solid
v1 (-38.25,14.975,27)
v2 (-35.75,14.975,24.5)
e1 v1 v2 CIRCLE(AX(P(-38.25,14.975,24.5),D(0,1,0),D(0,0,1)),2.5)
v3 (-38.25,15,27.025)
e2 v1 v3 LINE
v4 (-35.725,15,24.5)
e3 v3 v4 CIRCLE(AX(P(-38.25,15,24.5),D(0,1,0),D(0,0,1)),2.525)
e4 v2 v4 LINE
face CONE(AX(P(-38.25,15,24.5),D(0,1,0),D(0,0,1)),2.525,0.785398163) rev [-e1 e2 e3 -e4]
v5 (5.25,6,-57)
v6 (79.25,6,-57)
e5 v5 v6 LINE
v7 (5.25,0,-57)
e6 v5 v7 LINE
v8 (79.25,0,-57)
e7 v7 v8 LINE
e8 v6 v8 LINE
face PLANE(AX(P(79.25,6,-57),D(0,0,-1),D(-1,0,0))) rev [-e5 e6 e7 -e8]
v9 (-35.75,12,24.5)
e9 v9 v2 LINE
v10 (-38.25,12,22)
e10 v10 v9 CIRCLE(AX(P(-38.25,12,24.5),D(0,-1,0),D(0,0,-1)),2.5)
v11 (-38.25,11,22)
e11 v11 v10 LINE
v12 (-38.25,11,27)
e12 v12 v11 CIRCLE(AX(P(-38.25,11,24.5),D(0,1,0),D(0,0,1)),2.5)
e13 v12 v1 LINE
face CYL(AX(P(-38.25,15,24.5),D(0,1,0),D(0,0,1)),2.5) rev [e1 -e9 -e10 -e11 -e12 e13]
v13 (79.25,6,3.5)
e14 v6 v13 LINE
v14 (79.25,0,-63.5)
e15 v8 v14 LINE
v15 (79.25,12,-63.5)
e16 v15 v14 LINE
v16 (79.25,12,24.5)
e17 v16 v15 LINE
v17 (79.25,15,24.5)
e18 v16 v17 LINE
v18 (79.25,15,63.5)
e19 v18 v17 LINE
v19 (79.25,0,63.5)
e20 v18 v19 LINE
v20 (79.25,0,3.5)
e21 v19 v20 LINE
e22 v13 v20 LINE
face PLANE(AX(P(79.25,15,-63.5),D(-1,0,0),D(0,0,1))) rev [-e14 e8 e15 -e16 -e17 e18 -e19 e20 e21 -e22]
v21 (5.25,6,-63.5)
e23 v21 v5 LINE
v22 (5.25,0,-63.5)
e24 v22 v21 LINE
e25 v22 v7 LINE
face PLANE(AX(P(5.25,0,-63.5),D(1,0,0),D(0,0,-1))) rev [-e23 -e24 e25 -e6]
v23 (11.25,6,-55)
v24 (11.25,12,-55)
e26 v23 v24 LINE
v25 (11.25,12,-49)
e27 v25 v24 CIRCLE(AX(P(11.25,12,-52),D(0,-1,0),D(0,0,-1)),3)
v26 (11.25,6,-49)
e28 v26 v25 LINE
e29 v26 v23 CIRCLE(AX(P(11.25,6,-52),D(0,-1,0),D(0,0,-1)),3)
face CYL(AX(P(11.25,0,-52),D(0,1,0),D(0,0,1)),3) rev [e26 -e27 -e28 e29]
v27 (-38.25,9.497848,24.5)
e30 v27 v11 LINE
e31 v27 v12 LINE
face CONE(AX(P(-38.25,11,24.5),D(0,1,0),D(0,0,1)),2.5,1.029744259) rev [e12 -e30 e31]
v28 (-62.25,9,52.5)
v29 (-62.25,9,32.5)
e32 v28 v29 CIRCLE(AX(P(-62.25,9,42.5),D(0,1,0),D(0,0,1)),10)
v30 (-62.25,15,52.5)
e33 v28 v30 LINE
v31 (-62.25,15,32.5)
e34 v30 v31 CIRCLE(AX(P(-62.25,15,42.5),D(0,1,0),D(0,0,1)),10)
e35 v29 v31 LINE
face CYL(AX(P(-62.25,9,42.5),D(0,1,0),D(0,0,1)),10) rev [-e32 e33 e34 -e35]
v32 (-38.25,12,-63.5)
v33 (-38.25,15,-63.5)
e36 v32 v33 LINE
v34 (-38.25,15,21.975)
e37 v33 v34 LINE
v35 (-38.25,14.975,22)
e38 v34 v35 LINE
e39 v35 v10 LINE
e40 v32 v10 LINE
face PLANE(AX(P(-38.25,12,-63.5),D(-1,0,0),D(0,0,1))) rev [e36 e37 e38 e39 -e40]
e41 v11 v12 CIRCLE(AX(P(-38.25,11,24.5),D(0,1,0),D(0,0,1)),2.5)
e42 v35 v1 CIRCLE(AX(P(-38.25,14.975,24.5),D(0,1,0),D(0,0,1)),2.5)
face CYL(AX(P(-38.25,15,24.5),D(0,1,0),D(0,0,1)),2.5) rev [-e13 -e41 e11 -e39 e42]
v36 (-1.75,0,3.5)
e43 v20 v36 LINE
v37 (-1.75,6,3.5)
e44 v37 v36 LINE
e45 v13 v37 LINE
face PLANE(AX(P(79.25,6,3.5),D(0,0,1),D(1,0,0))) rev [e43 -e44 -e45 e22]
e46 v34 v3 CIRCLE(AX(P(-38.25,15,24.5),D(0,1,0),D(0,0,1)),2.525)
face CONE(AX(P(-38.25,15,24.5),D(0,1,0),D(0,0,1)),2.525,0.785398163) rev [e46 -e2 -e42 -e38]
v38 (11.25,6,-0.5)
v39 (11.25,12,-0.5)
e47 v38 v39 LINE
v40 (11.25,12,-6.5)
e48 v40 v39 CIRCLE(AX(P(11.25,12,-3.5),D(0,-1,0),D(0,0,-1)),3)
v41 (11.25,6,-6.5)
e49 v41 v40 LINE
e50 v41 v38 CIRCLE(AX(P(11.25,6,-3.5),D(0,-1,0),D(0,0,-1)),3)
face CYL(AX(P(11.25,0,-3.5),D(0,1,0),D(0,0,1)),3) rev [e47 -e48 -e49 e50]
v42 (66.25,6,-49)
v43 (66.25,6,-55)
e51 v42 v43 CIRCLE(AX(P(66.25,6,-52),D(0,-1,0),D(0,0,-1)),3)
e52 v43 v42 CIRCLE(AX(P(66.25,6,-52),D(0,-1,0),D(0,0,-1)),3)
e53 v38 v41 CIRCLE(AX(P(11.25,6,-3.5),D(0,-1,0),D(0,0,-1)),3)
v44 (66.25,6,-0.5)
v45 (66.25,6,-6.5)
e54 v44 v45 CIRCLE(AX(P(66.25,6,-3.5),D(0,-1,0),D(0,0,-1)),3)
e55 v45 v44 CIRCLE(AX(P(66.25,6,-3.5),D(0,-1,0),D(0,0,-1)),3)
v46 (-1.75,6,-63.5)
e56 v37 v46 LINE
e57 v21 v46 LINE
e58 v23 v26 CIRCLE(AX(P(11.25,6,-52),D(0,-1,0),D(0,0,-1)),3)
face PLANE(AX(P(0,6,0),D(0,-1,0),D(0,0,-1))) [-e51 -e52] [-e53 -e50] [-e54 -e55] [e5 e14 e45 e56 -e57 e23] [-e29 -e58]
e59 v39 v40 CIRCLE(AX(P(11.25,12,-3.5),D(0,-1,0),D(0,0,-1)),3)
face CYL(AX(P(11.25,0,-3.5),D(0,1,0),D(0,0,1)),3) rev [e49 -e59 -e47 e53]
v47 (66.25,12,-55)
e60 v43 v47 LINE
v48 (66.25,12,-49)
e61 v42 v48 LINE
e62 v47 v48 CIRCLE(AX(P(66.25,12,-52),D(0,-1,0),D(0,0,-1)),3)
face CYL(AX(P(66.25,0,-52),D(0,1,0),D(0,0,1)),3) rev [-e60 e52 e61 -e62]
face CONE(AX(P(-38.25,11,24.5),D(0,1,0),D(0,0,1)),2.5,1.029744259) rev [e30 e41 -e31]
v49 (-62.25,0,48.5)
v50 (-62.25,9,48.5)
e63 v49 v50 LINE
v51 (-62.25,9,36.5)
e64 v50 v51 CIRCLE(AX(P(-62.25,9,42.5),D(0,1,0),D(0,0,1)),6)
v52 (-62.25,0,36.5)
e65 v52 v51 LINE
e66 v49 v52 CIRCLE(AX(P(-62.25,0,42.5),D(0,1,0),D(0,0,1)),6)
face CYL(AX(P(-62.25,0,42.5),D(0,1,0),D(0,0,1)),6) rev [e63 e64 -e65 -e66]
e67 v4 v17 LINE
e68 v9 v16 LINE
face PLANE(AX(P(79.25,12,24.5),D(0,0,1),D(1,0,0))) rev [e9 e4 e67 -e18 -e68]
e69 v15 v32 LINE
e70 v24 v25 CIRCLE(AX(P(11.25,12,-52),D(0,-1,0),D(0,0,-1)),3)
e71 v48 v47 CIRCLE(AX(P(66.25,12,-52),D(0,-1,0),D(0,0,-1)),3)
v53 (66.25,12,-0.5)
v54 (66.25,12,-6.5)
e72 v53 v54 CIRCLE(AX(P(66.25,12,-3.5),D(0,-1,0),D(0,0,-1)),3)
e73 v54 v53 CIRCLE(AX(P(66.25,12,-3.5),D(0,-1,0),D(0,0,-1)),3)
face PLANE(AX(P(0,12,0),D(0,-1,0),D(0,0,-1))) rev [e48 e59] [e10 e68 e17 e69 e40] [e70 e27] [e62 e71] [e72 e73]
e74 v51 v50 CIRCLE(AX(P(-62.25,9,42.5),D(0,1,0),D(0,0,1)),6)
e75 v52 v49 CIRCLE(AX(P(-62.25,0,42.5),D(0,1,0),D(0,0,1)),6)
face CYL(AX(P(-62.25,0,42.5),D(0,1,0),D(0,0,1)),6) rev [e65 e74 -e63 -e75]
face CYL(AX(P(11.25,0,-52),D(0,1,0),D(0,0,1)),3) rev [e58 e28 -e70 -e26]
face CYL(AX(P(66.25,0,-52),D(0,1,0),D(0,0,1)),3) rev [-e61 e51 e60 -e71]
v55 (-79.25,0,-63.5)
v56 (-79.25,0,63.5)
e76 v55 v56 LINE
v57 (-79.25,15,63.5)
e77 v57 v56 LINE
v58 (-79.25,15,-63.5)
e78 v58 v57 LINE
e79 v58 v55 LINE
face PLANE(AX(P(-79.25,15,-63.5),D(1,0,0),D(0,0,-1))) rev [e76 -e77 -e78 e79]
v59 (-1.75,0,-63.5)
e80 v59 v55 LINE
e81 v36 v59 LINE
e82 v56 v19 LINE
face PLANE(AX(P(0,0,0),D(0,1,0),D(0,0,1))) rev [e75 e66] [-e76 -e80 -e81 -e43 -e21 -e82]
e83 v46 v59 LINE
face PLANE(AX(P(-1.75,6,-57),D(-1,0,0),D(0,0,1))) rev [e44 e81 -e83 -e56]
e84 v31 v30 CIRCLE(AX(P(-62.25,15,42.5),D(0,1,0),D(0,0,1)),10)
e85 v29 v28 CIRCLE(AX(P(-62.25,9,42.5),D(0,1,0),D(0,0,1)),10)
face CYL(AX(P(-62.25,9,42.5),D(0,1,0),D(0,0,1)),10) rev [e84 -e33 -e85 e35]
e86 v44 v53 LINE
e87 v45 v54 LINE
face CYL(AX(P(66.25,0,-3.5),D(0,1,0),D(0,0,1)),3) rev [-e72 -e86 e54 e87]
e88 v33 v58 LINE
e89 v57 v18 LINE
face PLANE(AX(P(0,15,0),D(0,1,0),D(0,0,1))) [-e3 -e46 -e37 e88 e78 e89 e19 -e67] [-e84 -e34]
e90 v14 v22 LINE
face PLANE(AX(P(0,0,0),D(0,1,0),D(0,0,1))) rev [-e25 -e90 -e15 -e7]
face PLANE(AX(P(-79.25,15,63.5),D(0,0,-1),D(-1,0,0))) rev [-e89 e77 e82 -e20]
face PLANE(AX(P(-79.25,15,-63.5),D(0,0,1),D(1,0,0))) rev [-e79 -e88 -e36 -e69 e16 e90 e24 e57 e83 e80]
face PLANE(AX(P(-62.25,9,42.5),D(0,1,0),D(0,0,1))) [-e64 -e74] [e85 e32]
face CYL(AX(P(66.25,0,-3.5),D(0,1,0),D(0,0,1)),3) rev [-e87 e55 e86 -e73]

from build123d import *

# Parameters (mm, degrees)
SKETCH1_W                              = 158.5
SKETCH1_H                              = 127
BOSS_EXTRUDE1_DEPTH                    = 15
SKETCH2_W                              = 117.5
SKETCH2_H                              = 88
CUT_EXTRUDE1_DEPTH                     = 3
SKETCH3_W                              = 81
SKETCH3_H                              = 60.5
CUT_EXTRUDE2_DEPTH                     = 6
SKETCH4_W                              = 7
SKETCH4_H                              = 6
CUT_EXTRUDE3_DEPTH                     = 103.653847955
SKETCH5_R                              = 3
CUT_EXTRUDE4_DEPTH                     = 103.653847955
SKETCH6_R                              = 10
CUT_EXTRUDE5_DEPTH                     = 6
SKETCH7_R                              = 6
CUT_EXTRUDE6_DEPTH                     = 102.950049044
F_5_0MM_BLIND_DOWEL_HOLE_1_D           = 5
F_5_0MM_BLIND_DOWEL_HOLE_1_DEPTH       = 4
F_5_0MM_BLIND_DOWEL_HOLE_1_CSINK_D     = 5.05
F_5_0MM_BLIND_DOWEL_HOLE_1_CSINK_ANGLE = 90
F_5_0MM_BLIND_DOWEL_HOLE_1_TIP         = 1.502151548


with BuildPart() as part:
    # Sketch1 → Boss-Extrude1 (new body)
    with BuildSketch(Plane(origin=(0, 0, 0), x_dir=(1, 0, 0), z_dir=(0, 1, 0))):
        Rectangle(SKETCH1_W, SKETCH1_H)
    extrude(amount=BOSS_EXTRUDE1_DEPTH)

    # Sketch2 → Cut-Extrude1 (cut)
    with BuildSketch(Plane(origin=(0, 15, 0), x_dir=(1, 0, 0), z_dir=(0, 1, 0))):
        with Locations((20.5, 19.5)):
            Rectangle(SKETCH2_W, SKETCH2_H)
    extrude(amount=-CUT_EXTRUDE1_DEPTH, mode=Mode.SUBTRACT)

    # Sketch3 → Cut-Extrude2 (cut)
    with BuildSketch(Plane.XZ):
        with Locations((38.75, -26.75)):
            Rectangle(SKETCH3_W, SKETCH3_H)
    extrude(amount=-CUT_EXTRUDE2_DEPTH, mode=Mode.SUBTRACT)

    # Sketch4 → Cut-Extrude3 (cut, through all)
    with BuildSketch(Plane.XY):
        with Locations((1.75, 3)):
            Rectangle(SKETCH4_W, SKETCH4_H)
    extrude(amount=-CUT_EXTRUDE3_DEPTH, mode=Mode.SUBTRACT)

    # Sketch5 → Cut-Extrude4 (cut, through all)
    with BuildSketch(Plane(origin=(0, 15, 0), x_dir=(1, 0, 0), z_dir=(0, 1, 0))):
        with Locations(Location((11.25, 52, 0), (0, 0, 90))):
            Circle(SKETCH5_R)
        with Locations(Location((66.25, 52, 0), (0, 0, 90))):
            Circle(SKETCH5_R)
        with Locations(Location((66.25, 3.5, 0), (0, 0, 90))):
            Circle(SKETCH5_R)
        with Locations(Location((11.25, 3.5, 0), (0, 0, 90))):
            Circle(SKETCH5_R)
    extrude(amount=-CUT_EXTRUDE4_DEPTH, mode=Mode.SUBTRACT)

    # Sketch6 → Cut-Extrude5 (cut)
    with BuildSketch(Plane(origin=(0, 15, 0), x_dir=(1, 0, 0), z_dir=(0, 1, 0))):
        with Locations(Location((-62.25, -42.5, 0), (0, 0, 270))):
            Circle(SKETCH6_R)
    extrude(amount=-CUT_EXTRUDE5_DEPTH, mode=Mode.SUBTRACT)

    # Sketch7 → Cut-Extrude6 (cut, through all)
    with BuildSketch(Plane(origin=(0, 9, 0), x_dir=(1, 0, 0), z_dir=(0, 1, 0))):
        with Locations(Location((-62.25, -42.5, 0), (0, 0, 270))):
            Circle(SKETCH7_R)
    extrude(amount=-CUT_EXTRUDE6_DEPTH, mode=Mode.SUBTRACT)

    # Ø5.0mm blind dowel hole 1
    with Locations(Plane(origin=(0, 15, 0), x_dir=(1, 0, 0), z_dir=(0, 1, 0))):
        with Locations((-38.25, -24.5)):
            CounterSinkHole(F_5_0MM_BLIND_DOWEL_HOLE_1_D / 2, F_5_0MM_BLIND_DOWEL_HOLE_1_CSINK_D / 2, depth=F_5_0MM_BLIND_DOWEL_HOLE_1_DEPTH, counter_sink_angle=F_5_0MM_BLIND_DOWEL_HOLE_1_CSINK_ANGLE)
            with Locations((0, 0, -(F_5_0MM_BLIND_DOWEL_HOLE_1_DEPTH + F_5_0MM_BLIND_DOWEL_HOLE_1_TIP / 2))):  # 118° drill point
                Cone(0, F_5_0MM_BLIND_DOWEL_HOLE_1_D / 2, F_5_0MM_BLIND_DOWEL_HOLE_1_TIP, mode=Mode.SUBTRACT)


solid = part.part
